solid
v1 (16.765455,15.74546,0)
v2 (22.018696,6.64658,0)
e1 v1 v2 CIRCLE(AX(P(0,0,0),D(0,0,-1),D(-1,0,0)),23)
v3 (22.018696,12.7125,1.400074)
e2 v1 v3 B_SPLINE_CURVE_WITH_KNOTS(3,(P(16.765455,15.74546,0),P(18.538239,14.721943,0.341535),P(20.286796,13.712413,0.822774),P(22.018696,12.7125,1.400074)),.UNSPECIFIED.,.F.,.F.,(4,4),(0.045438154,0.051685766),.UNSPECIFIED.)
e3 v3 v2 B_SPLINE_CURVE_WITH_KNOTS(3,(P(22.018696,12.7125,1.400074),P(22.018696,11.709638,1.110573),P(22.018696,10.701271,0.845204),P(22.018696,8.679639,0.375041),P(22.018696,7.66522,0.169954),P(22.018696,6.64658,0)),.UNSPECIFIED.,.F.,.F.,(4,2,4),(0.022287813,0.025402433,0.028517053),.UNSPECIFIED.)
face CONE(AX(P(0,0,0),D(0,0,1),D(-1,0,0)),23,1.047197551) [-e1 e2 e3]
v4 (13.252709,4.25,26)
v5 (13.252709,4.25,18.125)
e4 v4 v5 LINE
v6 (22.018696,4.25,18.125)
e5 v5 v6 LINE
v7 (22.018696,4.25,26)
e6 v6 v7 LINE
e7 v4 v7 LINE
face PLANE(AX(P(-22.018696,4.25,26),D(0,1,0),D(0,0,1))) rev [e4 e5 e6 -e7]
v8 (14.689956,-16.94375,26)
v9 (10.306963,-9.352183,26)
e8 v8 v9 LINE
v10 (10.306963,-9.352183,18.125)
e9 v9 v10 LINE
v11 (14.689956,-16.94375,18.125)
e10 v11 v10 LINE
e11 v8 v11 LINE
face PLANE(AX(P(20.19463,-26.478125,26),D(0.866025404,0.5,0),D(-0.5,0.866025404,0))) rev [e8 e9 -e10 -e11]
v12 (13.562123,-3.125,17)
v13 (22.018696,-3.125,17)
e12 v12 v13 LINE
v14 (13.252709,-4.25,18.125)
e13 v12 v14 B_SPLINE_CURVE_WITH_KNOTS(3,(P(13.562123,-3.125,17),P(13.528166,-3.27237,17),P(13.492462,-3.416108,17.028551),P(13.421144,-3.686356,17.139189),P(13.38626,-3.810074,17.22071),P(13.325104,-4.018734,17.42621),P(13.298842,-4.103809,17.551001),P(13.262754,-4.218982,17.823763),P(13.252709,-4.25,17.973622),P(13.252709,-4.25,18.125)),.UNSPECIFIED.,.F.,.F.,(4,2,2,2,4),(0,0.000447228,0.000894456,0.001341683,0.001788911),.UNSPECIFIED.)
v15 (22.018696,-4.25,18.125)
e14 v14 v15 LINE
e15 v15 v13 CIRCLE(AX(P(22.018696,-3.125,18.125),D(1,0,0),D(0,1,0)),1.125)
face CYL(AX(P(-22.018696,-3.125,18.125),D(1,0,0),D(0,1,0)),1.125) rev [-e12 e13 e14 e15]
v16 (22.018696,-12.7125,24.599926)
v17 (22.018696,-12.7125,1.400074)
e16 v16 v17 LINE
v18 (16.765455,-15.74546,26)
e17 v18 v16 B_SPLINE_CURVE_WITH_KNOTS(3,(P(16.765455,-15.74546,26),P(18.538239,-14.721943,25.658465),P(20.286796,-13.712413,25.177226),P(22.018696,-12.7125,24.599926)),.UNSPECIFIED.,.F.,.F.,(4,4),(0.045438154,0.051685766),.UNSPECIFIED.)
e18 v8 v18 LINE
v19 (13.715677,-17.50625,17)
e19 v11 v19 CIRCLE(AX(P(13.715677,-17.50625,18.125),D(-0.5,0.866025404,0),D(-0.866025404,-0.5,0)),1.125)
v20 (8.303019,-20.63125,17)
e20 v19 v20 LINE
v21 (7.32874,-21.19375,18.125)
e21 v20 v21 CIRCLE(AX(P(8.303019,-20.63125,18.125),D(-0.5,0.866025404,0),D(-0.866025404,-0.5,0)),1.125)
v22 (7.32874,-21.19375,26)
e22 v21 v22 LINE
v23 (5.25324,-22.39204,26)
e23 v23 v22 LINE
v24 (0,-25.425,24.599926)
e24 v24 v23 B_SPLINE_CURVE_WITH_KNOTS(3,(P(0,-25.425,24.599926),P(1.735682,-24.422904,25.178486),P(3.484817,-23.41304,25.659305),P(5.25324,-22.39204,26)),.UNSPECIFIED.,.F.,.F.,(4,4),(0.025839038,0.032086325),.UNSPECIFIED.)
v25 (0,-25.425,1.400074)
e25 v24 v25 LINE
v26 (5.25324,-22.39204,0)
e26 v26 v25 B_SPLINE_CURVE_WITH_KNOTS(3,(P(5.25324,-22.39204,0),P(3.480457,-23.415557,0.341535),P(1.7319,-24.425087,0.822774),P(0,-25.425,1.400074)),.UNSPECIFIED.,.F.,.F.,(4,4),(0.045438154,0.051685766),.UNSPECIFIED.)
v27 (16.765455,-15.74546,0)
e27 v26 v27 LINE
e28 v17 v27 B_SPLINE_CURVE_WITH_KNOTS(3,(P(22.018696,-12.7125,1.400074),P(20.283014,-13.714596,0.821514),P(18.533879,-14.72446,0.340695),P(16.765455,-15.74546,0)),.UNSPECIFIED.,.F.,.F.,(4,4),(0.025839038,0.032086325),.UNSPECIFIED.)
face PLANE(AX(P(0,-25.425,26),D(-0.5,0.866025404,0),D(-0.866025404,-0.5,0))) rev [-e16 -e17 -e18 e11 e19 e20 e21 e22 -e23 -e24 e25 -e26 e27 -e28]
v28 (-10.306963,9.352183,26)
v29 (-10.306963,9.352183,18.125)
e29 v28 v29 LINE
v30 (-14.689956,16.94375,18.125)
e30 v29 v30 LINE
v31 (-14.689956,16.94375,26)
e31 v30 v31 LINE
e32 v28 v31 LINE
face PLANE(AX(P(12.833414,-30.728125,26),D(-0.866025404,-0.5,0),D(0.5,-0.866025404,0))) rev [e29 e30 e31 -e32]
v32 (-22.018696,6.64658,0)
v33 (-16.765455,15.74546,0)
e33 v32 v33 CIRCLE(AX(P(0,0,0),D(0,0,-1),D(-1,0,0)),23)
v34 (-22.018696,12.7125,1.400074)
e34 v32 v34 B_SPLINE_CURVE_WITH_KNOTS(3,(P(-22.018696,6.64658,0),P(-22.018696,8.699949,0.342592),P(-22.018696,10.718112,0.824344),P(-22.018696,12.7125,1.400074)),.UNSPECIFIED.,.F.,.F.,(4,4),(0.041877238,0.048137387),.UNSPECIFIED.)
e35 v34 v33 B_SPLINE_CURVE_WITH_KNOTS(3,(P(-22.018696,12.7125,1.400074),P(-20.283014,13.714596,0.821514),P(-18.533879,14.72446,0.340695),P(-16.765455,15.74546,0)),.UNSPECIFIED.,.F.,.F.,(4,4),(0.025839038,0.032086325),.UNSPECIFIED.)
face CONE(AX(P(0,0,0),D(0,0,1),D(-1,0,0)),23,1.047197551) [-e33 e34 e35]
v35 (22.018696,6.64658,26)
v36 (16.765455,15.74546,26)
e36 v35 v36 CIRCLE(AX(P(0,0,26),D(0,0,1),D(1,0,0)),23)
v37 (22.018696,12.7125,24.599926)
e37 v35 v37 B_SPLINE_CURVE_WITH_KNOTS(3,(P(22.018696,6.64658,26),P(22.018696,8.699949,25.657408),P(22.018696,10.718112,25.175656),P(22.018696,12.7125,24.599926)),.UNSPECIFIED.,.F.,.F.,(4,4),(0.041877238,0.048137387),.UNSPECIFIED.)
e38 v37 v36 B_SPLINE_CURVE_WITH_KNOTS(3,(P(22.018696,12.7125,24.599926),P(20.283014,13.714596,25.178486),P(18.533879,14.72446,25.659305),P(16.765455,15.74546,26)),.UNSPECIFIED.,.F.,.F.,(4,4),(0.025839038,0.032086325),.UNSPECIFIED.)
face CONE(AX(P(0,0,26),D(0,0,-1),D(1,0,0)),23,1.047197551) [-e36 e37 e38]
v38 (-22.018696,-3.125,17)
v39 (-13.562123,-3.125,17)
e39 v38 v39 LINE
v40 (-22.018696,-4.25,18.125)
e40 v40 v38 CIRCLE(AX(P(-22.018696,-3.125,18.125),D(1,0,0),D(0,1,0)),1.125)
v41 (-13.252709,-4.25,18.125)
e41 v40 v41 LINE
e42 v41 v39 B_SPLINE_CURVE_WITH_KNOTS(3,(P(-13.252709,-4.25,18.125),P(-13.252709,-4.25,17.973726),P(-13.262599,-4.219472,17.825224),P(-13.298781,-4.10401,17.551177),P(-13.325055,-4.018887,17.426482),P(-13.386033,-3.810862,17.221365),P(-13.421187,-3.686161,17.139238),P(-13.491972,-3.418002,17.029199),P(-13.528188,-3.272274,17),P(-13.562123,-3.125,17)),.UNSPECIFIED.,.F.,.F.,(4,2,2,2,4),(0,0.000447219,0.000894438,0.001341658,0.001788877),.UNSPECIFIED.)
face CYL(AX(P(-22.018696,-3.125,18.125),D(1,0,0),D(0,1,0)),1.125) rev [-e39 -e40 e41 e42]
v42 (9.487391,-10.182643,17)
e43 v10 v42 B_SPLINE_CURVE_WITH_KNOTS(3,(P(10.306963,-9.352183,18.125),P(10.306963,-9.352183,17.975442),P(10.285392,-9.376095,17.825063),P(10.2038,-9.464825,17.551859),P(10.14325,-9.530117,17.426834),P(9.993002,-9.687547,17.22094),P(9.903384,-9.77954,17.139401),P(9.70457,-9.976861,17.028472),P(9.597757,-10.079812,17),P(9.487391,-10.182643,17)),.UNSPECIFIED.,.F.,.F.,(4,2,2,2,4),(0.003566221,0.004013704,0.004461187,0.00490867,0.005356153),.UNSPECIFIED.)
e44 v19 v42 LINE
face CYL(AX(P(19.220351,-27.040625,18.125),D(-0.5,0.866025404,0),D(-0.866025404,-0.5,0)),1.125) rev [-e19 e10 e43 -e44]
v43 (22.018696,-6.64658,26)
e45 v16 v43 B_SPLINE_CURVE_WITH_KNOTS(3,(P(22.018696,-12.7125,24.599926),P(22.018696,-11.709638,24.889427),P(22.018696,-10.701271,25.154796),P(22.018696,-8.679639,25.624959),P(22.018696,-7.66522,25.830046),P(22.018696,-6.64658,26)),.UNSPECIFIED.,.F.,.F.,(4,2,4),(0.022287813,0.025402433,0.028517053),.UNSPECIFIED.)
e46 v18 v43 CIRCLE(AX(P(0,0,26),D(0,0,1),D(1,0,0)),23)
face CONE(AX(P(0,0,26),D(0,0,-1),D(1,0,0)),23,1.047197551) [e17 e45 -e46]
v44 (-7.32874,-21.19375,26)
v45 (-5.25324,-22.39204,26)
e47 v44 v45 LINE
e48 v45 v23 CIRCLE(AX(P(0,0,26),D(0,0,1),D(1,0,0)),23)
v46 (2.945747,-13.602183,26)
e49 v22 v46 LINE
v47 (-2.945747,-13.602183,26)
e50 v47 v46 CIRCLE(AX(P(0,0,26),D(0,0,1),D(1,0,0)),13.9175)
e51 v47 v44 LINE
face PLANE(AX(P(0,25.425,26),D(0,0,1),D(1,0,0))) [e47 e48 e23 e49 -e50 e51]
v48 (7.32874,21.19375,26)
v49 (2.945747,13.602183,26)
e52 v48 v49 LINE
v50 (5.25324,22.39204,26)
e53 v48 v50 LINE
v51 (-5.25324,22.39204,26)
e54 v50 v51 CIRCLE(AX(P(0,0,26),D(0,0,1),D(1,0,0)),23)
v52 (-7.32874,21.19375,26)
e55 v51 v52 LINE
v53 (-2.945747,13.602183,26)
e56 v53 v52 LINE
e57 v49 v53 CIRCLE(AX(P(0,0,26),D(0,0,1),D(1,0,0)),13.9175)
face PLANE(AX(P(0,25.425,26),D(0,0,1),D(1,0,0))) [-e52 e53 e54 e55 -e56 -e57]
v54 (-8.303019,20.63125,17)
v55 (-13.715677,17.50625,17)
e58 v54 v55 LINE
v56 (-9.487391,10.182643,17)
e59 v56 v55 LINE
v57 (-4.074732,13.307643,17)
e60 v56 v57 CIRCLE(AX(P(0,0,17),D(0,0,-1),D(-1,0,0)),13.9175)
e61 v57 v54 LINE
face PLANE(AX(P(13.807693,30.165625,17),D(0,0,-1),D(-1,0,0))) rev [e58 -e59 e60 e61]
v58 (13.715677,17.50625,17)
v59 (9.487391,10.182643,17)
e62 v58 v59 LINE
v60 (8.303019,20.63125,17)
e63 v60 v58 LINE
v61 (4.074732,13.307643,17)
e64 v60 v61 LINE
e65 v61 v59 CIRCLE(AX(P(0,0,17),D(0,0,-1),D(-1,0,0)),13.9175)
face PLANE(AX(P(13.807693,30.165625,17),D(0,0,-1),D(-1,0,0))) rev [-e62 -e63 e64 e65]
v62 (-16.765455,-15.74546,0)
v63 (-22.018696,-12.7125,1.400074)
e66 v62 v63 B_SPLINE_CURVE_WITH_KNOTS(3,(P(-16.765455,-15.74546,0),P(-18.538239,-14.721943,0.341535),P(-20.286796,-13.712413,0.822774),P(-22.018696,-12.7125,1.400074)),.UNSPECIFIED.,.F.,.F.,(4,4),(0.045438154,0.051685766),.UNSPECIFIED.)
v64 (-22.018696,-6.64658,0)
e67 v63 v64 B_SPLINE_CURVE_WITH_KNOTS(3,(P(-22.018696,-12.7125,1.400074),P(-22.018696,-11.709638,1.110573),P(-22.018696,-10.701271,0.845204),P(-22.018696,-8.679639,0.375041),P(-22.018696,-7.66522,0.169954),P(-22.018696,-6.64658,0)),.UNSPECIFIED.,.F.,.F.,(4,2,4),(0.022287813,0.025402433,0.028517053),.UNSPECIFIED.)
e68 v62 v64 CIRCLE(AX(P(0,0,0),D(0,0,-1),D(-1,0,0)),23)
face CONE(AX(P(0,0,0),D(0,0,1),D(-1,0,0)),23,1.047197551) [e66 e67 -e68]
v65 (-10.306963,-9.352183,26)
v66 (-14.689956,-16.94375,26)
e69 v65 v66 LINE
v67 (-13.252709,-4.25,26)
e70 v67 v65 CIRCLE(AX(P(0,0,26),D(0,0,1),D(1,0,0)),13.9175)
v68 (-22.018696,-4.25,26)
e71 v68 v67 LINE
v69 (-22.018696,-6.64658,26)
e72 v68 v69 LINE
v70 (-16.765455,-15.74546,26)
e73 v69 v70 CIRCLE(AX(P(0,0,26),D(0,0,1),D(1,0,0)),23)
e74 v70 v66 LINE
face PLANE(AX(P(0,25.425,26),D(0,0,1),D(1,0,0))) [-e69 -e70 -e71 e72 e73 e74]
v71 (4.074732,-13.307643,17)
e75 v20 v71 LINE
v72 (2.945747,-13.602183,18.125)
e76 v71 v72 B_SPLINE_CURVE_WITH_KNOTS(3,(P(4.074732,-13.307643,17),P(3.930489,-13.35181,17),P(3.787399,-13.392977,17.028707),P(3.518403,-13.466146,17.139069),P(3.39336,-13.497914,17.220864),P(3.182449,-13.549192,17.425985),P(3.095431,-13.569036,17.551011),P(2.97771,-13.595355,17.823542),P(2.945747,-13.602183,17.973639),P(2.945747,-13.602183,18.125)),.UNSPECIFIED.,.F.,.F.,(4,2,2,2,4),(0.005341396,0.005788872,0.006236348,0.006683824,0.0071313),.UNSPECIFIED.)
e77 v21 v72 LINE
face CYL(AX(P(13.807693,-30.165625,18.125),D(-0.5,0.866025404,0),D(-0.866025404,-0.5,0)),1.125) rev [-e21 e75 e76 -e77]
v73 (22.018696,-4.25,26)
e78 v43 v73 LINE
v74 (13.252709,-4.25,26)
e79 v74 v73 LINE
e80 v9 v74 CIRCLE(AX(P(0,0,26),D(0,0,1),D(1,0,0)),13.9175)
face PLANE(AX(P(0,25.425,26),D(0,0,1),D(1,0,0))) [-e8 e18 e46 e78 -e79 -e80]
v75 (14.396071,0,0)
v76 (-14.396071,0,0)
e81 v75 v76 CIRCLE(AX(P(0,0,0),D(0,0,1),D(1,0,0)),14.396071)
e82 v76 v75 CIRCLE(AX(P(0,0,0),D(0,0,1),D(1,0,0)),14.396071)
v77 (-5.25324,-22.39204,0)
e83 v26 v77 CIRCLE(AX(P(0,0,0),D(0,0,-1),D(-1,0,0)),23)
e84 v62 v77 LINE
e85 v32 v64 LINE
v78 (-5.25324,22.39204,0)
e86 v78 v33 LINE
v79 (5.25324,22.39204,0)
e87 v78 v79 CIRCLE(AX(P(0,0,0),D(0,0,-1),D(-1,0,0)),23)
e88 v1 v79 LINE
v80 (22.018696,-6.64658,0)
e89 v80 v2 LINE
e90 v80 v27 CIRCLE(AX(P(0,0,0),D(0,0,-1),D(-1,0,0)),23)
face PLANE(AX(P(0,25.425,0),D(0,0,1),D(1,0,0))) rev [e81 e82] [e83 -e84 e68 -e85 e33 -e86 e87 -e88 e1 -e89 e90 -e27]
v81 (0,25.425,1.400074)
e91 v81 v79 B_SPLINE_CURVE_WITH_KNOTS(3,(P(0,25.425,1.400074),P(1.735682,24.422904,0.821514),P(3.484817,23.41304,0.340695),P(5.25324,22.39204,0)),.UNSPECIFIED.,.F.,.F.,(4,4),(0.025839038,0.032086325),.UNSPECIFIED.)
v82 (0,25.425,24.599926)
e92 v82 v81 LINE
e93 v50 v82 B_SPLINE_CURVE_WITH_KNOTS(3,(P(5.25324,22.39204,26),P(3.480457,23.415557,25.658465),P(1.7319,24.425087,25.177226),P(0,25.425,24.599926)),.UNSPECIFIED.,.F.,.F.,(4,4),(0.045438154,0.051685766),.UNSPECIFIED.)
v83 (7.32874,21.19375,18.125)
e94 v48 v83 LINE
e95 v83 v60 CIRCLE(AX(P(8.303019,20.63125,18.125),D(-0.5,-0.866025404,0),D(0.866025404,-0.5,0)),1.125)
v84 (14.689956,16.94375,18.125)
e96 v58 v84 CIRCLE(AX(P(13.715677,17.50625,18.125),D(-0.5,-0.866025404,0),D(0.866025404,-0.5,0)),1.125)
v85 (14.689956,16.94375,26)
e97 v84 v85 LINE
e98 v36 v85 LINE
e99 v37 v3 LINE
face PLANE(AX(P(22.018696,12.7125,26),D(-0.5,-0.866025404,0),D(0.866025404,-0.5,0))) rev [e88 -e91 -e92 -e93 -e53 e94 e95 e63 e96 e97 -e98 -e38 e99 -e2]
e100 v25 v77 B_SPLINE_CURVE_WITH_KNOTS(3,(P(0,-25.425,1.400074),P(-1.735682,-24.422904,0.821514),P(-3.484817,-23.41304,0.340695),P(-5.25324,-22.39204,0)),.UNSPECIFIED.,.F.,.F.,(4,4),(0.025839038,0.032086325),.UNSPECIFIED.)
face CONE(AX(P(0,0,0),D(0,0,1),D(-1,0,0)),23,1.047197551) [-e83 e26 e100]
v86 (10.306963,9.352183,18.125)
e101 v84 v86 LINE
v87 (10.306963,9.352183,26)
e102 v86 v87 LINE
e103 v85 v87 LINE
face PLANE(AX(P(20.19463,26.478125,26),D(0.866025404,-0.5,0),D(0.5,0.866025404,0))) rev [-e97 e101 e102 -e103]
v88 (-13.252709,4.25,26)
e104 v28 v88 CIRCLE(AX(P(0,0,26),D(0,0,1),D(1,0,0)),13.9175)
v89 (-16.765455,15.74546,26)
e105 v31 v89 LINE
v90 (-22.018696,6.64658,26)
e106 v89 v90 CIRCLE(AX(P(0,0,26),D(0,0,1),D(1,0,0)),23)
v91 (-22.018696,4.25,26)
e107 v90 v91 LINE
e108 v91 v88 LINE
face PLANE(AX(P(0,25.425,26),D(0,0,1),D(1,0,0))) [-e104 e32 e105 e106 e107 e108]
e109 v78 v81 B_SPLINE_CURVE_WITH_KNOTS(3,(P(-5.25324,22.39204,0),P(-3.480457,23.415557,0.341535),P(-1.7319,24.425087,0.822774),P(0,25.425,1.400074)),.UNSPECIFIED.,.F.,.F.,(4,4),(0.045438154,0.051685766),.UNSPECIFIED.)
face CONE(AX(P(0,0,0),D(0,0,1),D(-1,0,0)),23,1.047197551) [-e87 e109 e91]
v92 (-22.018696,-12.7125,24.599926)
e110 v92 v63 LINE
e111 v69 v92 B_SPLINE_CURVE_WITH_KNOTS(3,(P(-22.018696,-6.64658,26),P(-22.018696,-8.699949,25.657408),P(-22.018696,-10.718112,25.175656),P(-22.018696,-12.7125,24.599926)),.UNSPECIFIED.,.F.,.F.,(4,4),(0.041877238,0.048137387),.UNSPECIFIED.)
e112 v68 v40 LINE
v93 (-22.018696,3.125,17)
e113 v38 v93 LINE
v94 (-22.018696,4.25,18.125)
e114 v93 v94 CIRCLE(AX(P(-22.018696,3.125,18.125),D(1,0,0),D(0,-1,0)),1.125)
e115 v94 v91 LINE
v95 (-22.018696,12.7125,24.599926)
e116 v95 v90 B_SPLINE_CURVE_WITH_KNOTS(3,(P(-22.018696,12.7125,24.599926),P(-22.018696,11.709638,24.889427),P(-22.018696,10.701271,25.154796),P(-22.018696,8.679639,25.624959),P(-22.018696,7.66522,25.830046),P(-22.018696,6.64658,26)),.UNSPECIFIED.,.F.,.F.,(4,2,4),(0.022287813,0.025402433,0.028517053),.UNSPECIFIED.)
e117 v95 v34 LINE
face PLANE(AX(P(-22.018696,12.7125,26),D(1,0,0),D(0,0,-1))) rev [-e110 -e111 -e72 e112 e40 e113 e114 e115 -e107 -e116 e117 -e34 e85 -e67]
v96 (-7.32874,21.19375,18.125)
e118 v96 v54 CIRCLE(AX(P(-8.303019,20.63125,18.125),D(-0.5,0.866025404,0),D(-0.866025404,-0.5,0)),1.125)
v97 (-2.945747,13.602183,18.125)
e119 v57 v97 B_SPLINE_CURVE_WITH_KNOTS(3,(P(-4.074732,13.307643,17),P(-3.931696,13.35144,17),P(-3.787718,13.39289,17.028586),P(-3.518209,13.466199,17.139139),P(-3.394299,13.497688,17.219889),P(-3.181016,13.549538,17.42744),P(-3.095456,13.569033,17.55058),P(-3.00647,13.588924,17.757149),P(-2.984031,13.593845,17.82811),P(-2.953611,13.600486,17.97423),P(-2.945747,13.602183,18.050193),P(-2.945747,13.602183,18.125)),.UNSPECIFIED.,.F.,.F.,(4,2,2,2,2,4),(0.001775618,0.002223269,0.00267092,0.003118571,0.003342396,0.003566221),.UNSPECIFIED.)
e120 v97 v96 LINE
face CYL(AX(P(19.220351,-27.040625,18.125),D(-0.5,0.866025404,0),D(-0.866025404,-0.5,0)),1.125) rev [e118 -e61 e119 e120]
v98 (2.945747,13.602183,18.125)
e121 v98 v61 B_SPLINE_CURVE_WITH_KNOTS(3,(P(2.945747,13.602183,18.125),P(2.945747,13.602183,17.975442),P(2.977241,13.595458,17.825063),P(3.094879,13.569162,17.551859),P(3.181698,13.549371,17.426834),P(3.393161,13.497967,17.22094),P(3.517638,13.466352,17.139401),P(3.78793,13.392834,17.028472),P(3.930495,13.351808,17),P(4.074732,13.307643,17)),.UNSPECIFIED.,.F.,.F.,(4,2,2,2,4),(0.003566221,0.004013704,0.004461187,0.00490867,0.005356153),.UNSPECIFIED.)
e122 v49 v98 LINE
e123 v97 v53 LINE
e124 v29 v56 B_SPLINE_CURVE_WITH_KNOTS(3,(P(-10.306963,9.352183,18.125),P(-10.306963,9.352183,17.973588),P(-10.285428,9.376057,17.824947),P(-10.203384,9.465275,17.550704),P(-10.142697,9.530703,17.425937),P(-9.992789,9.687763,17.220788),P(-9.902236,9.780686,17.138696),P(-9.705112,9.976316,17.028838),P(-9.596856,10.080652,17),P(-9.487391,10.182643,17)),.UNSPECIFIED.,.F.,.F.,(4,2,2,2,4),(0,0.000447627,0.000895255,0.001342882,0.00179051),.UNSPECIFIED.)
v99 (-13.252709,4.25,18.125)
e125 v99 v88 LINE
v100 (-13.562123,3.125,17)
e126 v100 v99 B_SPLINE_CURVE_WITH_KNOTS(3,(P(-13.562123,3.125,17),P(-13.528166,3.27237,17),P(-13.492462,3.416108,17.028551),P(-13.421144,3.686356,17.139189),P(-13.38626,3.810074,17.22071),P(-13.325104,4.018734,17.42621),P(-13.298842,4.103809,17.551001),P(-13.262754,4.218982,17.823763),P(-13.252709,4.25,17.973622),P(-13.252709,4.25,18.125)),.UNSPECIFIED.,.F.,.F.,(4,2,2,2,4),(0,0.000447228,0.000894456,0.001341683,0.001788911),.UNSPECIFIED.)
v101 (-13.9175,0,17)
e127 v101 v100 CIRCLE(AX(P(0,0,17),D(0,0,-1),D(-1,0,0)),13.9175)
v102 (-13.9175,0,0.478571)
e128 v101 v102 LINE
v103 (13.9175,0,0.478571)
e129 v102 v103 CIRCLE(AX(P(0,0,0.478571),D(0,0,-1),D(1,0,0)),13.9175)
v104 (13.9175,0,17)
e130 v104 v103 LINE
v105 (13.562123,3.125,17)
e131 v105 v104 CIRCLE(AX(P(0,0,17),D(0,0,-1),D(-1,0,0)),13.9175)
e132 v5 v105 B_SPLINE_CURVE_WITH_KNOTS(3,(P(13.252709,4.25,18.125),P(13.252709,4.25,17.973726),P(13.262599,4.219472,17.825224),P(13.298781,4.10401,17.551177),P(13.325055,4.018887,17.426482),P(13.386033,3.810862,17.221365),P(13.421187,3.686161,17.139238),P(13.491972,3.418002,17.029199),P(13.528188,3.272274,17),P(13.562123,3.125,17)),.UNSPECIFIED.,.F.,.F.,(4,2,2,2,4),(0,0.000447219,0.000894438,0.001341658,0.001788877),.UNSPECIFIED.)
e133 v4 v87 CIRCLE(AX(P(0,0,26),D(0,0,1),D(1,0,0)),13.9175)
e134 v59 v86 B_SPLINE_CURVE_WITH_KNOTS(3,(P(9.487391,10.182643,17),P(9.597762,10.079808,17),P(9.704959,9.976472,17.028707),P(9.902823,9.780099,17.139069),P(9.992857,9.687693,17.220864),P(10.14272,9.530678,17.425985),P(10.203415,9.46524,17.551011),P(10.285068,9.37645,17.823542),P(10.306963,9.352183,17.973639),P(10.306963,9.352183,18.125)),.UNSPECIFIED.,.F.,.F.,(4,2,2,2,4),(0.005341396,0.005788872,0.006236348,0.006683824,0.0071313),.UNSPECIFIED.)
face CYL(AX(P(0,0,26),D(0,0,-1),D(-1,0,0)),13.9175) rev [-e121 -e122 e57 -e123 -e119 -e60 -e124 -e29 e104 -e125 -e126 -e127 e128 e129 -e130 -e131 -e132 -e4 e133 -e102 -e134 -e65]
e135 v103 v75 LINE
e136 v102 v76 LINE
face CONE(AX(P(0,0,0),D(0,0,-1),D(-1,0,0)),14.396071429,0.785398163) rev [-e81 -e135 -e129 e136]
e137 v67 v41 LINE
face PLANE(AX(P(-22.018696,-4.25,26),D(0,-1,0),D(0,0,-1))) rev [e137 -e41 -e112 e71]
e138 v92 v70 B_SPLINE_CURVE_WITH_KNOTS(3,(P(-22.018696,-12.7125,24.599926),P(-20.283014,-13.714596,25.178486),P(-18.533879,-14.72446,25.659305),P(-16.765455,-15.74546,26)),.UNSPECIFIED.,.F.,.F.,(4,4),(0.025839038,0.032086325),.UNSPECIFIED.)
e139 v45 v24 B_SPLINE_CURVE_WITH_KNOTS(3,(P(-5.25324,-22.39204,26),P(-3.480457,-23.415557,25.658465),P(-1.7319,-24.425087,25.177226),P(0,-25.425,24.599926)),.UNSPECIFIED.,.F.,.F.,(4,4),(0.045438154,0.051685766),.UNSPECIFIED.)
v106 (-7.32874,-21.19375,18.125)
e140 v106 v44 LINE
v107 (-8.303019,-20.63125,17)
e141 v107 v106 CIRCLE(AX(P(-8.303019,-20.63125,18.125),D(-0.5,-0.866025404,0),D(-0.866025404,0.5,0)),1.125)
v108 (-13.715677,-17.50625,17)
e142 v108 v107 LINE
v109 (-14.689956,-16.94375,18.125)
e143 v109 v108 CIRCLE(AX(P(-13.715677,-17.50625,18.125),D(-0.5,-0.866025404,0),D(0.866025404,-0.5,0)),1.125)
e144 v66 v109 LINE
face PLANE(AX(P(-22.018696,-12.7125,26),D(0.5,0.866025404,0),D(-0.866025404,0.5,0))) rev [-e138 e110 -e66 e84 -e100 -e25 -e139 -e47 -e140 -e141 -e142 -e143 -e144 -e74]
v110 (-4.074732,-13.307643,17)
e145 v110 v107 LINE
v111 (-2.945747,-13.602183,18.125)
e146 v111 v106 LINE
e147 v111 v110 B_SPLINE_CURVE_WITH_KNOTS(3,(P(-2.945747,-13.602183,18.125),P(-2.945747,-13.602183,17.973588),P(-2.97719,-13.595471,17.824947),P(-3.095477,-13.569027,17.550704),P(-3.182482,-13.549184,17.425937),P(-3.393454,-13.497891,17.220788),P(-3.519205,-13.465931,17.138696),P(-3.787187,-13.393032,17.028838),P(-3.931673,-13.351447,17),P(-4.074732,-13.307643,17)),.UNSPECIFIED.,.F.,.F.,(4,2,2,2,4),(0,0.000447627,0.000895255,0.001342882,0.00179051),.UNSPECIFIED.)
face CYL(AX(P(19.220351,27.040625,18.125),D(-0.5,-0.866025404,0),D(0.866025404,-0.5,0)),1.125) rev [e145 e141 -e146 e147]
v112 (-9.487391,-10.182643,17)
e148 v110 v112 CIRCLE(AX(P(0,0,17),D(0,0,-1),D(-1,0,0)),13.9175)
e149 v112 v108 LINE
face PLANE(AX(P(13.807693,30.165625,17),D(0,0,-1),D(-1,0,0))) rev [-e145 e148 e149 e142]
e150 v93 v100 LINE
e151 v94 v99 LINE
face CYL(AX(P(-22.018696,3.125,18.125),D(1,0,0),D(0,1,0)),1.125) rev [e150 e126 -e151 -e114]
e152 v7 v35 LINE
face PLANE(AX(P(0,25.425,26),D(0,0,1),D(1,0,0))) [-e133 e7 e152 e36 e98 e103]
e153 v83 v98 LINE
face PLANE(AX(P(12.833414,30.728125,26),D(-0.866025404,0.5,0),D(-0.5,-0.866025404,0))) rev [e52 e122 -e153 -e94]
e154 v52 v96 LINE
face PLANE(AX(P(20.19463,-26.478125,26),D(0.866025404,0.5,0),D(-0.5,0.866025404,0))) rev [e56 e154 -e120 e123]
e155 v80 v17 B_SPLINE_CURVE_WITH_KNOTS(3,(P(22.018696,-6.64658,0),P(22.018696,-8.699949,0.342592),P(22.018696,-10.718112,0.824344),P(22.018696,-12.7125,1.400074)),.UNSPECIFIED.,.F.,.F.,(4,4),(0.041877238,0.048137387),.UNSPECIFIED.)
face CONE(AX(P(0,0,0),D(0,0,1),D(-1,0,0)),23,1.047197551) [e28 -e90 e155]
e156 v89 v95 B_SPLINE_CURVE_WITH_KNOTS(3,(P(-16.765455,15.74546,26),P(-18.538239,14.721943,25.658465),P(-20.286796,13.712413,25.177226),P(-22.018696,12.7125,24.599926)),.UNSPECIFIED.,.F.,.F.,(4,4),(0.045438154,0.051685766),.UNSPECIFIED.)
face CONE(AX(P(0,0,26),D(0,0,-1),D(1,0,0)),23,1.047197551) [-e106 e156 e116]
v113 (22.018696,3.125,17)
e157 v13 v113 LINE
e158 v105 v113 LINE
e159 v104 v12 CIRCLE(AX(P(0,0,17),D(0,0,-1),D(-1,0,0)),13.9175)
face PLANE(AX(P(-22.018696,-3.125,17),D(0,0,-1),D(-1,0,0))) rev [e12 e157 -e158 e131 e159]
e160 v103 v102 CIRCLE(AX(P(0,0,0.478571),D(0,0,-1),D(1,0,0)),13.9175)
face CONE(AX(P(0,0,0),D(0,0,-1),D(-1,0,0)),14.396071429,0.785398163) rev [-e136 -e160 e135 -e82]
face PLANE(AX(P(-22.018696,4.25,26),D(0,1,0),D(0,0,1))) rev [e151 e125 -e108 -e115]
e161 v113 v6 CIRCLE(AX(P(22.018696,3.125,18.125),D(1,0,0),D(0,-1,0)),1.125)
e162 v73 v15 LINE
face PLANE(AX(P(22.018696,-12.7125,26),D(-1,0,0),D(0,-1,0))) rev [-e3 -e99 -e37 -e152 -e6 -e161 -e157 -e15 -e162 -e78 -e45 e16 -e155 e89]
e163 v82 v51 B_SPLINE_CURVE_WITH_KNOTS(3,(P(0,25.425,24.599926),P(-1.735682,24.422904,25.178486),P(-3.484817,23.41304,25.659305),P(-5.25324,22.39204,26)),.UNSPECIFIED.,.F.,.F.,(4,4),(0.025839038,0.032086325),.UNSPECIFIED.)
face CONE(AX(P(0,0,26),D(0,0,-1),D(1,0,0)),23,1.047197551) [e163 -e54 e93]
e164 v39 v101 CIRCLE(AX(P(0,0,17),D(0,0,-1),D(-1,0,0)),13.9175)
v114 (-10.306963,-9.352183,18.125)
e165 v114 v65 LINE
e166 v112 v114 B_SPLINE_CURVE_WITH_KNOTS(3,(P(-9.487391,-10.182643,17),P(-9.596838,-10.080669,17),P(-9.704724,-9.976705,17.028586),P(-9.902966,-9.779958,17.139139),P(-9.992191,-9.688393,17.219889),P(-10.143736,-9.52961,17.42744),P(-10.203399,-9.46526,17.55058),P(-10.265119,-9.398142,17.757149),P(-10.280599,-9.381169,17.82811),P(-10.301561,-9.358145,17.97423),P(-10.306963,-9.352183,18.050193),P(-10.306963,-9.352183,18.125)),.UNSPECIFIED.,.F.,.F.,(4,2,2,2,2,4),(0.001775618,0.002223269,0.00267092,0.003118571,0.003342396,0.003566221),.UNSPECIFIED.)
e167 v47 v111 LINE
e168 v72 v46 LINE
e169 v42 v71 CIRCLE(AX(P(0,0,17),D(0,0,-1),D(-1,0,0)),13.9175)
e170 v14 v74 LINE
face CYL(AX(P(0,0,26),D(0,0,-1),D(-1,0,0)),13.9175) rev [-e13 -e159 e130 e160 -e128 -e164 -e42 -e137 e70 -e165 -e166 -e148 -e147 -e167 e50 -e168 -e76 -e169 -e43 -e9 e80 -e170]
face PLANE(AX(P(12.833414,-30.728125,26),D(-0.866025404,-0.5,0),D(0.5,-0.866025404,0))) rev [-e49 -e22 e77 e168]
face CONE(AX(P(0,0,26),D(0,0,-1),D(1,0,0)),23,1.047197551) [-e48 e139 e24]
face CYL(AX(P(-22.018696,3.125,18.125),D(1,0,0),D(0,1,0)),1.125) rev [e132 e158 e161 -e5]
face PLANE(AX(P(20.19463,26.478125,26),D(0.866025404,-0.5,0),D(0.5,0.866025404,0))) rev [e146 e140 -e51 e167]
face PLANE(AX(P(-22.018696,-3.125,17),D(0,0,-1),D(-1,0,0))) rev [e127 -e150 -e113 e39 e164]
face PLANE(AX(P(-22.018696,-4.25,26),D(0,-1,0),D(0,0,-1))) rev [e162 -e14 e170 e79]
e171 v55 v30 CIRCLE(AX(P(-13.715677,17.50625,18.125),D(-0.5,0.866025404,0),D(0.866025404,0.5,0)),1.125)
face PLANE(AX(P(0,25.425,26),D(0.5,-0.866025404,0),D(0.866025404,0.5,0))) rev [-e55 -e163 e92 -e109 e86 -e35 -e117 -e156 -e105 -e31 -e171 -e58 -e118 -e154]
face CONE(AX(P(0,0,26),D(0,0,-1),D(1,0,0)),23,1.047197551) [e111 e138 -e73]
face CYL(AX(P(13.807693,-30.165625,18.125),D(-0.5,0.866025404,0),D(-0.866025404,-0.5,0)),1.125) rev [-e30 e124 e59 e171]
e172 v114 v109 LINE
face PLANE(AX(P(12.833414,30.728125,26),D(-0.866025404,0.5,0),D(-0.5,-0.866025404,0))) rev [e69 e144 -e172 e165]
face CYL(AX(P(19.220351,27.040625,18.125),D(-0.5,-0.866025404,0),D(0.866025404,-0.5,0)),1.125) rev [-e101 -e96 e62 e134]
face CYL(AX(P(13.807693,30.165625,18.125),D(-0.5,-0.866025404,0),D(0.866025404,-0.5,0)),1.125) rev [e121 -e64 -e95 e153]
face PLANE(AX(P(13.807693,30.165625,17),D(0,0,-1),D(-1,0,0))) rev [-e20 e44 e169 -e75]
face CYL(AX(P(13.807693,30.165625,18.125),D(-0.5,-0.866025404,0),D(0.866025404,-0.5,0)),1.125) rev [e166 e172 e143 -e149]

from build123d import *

# Parameters (mm, degrees)
SKETCH_1_R               = 13.9175
EXTRUDE_816_DEPTH        = 26
SKETCH_2_OUTSIDE_W       = 211.19
SKETCH_2_OUTSIDE_H       = 218.002
SKETCH_2_OUTSIDE_R       = 23
CUT_EXTRUDE_1_DEPTH      = 43.511805346
CUT_EXTRUDE_1_DRAFT      = -60
SKETCH_3_OUTSIDE_W       = 211.19
SKETCH_3_OUTSIDE_H       = 218.002
SKETCH_3_OUTSIDE_R       = 23
CUT_EXTRUDE_2_DEPTH      = 43.511805346
CUT_EXTRUDE_2_DRAFT      = -60
CUT_EXTRUDE_3_DEPTH      = 58.111491838
PATTERN_CIRCULAR_1_COUNT = 3
CHAMFER_1_SIZE           = 0.478571429


with BuildPart() as part:
    # 草图1 → Extrude 816 (new body)
    with BuildSketch(Plane.XY):
        Polygon((0, 25.425), (-22.018695891, 12.7125), (-22.018695891, -12.7125), (0, -25.425), (22.018695891, -12.7125), (22.018695891, 12.7125), align=None)
        with Locations(Location((0, 0, 0), (0, 0, 180))):
            Circle(SKETCH_1_R, mode=Mode.SUBTRACT)
    extrude(amount=EXTRUDE_816_DEPTH)


with BuildPart() as cut_extrude_1_tool:
    # 草图2 outside → 切除-拉伸1 (with draft: the straight prism first)
    with BuildSketch(Plane(origin=(0, 0, 0), x_dir=(-1, 0, 0), z_dir=(0, 0, -1))):
        Rectangle(SKETCH_2_OUTSIDE_W, SKETCH_2_OUTSIDE_H)
        Circle(SKETCH_2_OUTSIDE_R, mode=Mode.SUBTRACT)
    extrude(amount=-CUT_EXTRUDE_1_DEPTH)
    # 切除-拉伸1: the draft: its side faces are tilted about the plane it starts from
    cut_extrude_1_sides = [cut_extrude_1_tool.faces().sort_by_distance(p)[0] for p in [
        (0, -109.001, 21.755902673),
        (-105.595, 0, 21.755902673),
        (0, 109.001, 21.755902673),
        (105.595, 0, 21.755902673),
        (23, 0, 21.755902673),
    ]]
    draft(cut_extrude_1_sides, Plane(origin=(0, 0, 0), x_dir=(-1, 0, 0), z_dir=(0, 0, -1)), CUT_EXTRUDE_1_DRAFT)


with BuildPart() as part_1:
    add(part.part)

    # 切除-拉伸1: cut by cut_extrude_1_tool
    add(cut_extrude_1_tool.part, mode=Mode.SUBTRACT)


with BuildPart() as cut_extrude_2_tool:
    # 草图3 outside → 切除-拉伸2 (with draft: the straight prism first)
    with BuildSketch(Plane.XY.offset(26)):
        Rectangle(SKETCH_3_OUTSIDE_W, SKETCH_3_OUTSIDE_H)
        Circle(SKETCH_3_OUTSIDE_R, mode=Mode.SUBTRACT)
    extrude(amount=-CUT_EXTRUDE_2_DEPTH)
    # 切除-拉伸2: the draft: its side faces are tilted about the plane it starts from
    cut_extrude_2_sides = [cut_extrude_2_tool.faces().sort_by_distance(p)[0] for p in [
        (0, -109.001, 4.244097327),
        (105.595, 0, 4.244097327),
        (0, 109.001, 4.244097327),
        (-105.595, 0, 4.244097327),
        (-23, 0, 4.244097327),
    ]]
    draft(cut_extrude_2_sides, Plane.XY.offset(26), CUT_EXTRUDE_2_DRAFT)


with BuildPart() as part_2:
    add(part_1.part)

    # 切除-拉伸2: cut by cut_extrude_2_tool
    add(cut_extrude_2_tool.part, mode=Mode.SUBTRACT)

    # 草图6 → 切除-拉伸3 (cut, through all)
    with BuildSketch(Plane(origin=(22.018695891, 0, 0), x_dir=(0, 0, -1), z_dir=(1, 0, 0))):
        with BuildLine():
            Line((-26, -4.25), (-26, 4.25))
            Line((-26, 4.25), (-18.125, 4.25))
            ThreePointArc((-18.125, 4.25), (-17.329504871, 3.920495129), (-17, 3.125))
            Line((-17, 3.125), (-17, -3.125))
            ThreePointArc((-17, -3.125), (-17.329504871, -3.920495129), (-18.125, -4.25))
            Line((-18.125, -4.25), (-26, -4.25))
        make_face()
    cut_extrude_3 = extrude(amount=-CUT_EXTRUDE_3_DEPTH, mode=Mode.SUBTRACT)

    # 阵列(圆周)1: 切除-拉伸3 ×3 about axis
    pattern_circular_1_axis = Axis((0, 0, 0), (0, 0, 1))
    for i in range(1, PATTERN_CIRCULAR_1_COUNT):
        add(cut_extrude_3.rotate(pattern_circular_1_axis, i * 360 / PATTERN_CIRCULAR_1_COUNT), mode=Mode.SUBTRACT)

    # 倒角1
    chamfer_1_edges = [part_2.edges().sort_by_distance(p)[0] for p in [
        (13.9175, 0, 0),
    ]]
    chamfer(chamfer_1_edges, length=CHAMFER_1_SIZE)


solid = part_2.part
